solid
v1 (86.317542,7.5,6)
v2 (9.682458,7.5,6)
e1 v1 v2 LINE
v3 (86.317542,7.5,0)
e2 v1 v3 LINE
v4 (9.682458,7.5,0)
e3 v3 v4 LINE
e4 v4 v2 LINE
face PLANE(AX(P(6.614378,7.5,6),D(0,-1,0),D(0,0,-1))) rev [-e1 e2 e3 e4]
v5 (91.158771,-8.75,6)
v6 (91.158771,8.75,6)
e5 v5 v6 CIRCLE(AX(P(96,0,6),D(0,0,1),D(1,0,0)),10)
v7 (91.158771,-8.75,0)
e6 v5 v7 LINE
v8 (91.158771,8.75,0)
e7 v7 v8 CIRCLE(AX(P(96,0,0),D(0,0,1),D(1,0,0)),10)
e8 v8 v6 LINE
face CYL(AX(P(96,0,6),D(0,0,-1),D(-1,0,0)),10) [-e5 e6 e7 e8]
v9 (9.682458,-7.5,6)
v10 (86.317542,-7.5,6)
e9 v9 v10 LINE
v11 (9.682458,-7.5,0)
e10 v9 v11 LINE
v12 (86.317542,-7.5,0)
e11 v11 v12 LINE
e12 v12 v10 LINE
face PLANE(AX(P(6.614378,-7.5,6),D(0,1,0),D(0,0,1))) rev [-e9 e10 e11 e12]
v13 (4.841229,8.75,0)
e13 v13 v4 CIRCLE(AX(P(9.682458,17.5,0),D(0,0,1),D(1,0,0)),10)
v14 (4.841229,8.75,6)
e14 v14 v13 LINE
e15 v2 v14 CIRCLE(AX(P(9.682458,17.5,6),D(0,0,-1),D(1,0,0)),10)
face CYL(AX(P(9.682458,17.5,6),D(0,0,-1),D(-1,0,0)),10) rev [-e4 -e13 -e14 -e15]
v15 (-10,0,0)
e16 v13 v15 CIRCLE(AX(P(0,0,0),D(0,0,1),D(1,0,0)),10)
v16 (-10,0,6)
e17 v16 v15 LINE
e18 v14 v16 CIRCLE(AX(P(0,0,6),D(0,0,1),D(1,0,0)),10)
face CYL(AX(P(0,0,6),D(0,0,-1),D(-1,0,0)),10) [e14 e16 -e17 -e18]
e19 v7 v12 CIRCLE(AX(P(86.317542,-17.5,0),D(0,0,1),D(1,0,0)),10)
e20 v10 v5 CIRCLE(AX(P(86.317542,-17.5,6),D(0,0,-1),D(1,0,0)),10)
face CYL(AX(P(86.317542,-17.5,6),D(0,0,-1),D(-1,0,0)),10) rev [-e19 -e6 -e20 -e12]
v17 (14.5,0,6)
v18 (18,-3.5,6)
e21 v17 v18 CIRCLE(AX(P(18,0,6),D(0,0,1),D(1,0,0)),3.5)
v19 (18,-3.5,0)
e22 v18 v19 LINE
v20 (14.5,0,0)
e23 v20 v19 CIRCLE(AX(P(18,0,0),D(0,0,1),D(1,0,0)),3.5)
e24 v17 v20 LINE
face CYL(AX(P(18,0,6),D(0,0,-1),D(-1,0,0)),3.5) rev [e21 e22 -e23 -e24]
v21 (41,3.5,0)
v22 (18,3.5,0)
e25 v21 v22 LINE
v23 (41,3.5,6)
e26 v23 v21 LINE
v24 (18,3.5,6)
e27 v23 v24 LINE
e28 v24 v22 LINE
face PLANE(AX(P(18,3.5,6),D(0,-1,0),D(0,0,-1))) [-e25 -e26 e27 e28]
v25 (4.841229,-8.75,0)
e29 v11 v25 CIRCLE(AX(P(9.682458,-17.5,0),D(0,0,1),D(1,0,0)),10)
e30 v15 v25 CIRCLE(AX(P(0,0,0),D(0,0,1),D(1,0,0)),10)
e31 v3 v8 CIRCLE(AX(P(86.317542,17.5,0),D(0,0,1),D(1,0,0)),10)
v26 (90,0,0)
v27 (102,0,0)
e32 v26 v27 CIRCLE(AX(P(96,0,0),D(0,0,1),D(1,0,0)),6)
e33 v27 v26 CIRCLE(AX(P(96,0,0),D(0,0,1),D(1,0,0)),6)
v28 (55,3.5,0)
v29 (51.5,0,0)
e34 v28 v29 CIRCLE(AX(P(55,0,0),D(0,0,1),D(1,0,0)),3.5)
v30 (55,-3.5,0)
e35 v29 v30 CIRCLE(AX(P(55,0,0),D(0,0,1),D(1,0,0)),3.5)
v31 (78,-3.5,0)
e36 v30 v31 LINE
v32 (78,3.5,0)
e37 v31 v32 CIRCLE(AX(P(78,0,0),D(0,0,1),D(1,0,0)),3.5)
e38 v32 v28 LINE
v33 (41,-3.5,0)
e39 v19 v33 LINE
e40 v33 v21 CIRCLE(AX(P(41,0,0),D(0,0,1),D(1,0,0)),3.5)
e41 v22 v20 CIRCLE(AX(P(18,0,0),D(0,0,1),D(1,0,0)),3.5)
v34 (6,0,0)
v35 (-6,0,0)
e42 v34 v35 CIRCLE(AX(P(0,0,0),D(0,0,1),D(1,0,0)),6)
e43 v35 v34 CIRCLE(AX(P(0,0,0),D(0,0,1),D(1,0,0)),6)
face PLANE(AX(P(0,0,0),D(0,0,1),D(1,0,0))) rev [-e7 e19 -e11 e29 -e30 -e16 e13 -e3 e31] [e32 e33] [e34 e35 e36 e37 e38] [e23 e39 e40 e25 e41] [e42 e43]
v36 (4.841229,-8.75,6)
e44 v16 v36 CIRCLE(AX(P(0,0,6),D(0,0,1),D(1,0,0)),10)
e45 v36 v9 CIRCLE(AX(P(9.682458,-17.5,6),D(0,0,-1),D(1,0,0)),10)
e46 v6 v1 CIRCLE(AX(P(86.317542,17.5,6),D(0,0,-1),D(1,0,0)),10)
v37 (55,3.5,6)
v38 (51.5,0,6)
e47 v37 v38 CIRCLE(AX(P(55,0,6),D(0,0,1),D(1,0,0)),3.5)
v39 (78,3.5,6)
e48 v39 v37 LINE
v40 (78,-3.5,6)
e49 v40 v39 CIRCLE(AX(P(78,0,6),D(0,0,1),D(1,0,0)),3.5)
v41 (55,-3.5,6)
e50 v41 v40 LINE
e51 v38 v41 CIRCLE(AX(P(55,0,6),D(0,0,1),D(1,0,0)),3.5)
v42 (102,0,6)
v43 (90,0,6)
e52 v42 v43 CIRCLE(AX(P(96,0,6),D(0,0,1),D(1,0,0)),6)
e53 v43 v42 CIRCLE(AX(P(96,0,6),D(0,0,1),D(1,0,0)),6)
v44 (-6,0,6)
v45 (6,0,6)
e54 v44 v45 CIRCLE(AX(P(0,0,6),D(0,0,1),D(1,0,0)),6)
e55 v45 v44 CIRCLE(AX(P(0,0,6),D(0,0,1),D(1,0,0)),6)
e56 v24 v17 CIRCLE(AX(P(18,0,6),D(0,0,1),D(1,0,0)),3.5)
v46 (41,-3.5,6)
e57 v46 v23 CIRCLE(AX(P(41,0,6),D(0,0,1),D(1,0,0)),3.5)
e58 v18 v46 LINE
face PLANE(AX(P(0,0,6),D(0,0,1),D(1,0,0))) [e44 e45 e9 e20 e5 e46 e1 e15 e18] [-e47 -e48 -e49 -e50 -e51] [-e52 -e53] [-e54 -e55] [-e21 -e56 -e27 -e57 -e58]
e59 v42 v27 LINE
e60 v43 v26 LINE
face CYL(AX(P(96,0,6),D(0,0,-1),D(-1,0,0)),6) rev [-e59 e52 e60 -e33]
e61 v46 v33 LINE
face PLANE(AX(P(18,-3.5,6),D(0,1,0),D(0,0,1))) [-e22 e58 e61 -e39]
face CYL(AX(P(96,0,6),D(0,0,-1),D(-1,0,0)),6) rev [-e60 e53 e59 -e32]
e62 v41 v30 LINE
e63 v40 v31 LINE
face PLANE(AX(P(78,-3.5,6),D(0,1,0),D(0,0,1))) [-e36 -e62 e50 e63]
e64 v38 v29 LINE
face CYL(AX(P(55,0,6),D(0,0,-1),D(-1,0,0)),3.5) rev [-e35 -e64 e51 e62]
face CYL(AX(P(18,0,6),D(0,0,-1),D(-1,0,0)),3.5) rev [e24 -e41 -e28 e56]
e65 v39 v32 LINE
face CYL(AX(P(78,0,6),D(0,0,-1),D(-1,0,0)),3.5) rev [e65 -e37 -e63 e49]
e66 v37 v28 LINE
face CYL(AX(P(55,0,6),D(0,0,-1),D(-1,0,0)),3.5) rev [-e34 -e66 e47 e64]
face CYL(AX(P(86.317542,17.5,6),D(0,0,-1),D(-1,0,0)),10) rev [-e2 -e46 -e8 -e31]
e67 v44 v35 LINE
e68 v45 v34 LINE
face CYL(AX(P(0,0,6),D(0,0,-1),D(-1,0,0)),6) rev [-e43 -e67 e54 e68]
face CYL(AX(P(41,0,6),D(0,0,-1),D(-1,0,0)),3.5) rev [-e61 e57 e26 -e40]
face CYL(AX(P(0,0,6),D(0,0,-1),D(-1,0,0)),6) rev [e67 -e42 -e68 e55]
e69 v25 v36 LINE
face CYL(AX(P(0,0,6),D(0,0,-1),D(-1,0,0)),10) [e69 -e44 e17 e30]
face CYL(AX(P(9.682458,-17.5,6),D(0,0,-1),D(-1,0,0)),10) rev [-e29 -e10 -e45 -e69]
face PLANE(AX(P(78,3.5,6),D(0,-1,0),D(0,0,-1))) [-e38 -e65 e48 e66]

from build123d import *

# Parameters (mm, degrees)
SKETCH_1_R      = 6
EXTRUDE_1_DEPTH = 6
FILLET_R10_1_R  = 10


with BuildPart() as part:
    # 草图1 → 凸台-拉伸1 (new body)
    with BuildSketch(Plane.XY):
        with BuildLine():
            Line((6.614378278, 7.5), (89.385621722, 7.5))
            ThreePointArc((89.385621722, 7.5), (106, 0), (89.385621722, -7.5))
            Line((89.385621722, -7.5), (6.614378278, -7.5))
            ThreePointArc((6.614378278, -7.5), (-10, 0), (6.614378278, 7.5))
        make_face()
        Circle(SKETCH_1_R, mode=Mode.SUBTRACT)
        with Locations((96, 0)):
            Circle(SKETCH_1_R, mode=Mode.SUBTRACT)
        with BuildLine():
            Line((18, 3.5), (41, 3.5))
            ThreePointArc((41, 3.5), (44.5, 0), (41, -3.5))
            Line((41, -3.5), (18, -3.5))
            ThreePointArc((18, -3.5), (14.5, 0), (18, 3.5))
        make_face(mode=Mode.SUBTRACT)
        with BuildLine():
            Line((78, -3.5), (55, -3.5))
            ThreePointArc((55, -3.5), (51.5, 0), (55, 3.5))
            Line((55, 3.5), (78, 3.5))
            ThreePointArc((78, 3.5), (81.5, 0), (78, -3.5))
        make_face(mode=Mode.SUBTRACT)
    extrude(amount=EXTRUDE_1_DEPTH)

    # R10 圆角1
    fillet_r10_1_edges = [part.edges().sort_by_distance(p)[0] for p in [
        (6.614378278, 7.5, 3),
        (89.385621722, 7.5, 3),
        (89.385621722, -7.5, 3),
        (6.614378278, -7.5, 3),
    ]]
    fillet(fillet_r10_1_edges, radius=FILLET_R10_1_R)


solid = part.part
